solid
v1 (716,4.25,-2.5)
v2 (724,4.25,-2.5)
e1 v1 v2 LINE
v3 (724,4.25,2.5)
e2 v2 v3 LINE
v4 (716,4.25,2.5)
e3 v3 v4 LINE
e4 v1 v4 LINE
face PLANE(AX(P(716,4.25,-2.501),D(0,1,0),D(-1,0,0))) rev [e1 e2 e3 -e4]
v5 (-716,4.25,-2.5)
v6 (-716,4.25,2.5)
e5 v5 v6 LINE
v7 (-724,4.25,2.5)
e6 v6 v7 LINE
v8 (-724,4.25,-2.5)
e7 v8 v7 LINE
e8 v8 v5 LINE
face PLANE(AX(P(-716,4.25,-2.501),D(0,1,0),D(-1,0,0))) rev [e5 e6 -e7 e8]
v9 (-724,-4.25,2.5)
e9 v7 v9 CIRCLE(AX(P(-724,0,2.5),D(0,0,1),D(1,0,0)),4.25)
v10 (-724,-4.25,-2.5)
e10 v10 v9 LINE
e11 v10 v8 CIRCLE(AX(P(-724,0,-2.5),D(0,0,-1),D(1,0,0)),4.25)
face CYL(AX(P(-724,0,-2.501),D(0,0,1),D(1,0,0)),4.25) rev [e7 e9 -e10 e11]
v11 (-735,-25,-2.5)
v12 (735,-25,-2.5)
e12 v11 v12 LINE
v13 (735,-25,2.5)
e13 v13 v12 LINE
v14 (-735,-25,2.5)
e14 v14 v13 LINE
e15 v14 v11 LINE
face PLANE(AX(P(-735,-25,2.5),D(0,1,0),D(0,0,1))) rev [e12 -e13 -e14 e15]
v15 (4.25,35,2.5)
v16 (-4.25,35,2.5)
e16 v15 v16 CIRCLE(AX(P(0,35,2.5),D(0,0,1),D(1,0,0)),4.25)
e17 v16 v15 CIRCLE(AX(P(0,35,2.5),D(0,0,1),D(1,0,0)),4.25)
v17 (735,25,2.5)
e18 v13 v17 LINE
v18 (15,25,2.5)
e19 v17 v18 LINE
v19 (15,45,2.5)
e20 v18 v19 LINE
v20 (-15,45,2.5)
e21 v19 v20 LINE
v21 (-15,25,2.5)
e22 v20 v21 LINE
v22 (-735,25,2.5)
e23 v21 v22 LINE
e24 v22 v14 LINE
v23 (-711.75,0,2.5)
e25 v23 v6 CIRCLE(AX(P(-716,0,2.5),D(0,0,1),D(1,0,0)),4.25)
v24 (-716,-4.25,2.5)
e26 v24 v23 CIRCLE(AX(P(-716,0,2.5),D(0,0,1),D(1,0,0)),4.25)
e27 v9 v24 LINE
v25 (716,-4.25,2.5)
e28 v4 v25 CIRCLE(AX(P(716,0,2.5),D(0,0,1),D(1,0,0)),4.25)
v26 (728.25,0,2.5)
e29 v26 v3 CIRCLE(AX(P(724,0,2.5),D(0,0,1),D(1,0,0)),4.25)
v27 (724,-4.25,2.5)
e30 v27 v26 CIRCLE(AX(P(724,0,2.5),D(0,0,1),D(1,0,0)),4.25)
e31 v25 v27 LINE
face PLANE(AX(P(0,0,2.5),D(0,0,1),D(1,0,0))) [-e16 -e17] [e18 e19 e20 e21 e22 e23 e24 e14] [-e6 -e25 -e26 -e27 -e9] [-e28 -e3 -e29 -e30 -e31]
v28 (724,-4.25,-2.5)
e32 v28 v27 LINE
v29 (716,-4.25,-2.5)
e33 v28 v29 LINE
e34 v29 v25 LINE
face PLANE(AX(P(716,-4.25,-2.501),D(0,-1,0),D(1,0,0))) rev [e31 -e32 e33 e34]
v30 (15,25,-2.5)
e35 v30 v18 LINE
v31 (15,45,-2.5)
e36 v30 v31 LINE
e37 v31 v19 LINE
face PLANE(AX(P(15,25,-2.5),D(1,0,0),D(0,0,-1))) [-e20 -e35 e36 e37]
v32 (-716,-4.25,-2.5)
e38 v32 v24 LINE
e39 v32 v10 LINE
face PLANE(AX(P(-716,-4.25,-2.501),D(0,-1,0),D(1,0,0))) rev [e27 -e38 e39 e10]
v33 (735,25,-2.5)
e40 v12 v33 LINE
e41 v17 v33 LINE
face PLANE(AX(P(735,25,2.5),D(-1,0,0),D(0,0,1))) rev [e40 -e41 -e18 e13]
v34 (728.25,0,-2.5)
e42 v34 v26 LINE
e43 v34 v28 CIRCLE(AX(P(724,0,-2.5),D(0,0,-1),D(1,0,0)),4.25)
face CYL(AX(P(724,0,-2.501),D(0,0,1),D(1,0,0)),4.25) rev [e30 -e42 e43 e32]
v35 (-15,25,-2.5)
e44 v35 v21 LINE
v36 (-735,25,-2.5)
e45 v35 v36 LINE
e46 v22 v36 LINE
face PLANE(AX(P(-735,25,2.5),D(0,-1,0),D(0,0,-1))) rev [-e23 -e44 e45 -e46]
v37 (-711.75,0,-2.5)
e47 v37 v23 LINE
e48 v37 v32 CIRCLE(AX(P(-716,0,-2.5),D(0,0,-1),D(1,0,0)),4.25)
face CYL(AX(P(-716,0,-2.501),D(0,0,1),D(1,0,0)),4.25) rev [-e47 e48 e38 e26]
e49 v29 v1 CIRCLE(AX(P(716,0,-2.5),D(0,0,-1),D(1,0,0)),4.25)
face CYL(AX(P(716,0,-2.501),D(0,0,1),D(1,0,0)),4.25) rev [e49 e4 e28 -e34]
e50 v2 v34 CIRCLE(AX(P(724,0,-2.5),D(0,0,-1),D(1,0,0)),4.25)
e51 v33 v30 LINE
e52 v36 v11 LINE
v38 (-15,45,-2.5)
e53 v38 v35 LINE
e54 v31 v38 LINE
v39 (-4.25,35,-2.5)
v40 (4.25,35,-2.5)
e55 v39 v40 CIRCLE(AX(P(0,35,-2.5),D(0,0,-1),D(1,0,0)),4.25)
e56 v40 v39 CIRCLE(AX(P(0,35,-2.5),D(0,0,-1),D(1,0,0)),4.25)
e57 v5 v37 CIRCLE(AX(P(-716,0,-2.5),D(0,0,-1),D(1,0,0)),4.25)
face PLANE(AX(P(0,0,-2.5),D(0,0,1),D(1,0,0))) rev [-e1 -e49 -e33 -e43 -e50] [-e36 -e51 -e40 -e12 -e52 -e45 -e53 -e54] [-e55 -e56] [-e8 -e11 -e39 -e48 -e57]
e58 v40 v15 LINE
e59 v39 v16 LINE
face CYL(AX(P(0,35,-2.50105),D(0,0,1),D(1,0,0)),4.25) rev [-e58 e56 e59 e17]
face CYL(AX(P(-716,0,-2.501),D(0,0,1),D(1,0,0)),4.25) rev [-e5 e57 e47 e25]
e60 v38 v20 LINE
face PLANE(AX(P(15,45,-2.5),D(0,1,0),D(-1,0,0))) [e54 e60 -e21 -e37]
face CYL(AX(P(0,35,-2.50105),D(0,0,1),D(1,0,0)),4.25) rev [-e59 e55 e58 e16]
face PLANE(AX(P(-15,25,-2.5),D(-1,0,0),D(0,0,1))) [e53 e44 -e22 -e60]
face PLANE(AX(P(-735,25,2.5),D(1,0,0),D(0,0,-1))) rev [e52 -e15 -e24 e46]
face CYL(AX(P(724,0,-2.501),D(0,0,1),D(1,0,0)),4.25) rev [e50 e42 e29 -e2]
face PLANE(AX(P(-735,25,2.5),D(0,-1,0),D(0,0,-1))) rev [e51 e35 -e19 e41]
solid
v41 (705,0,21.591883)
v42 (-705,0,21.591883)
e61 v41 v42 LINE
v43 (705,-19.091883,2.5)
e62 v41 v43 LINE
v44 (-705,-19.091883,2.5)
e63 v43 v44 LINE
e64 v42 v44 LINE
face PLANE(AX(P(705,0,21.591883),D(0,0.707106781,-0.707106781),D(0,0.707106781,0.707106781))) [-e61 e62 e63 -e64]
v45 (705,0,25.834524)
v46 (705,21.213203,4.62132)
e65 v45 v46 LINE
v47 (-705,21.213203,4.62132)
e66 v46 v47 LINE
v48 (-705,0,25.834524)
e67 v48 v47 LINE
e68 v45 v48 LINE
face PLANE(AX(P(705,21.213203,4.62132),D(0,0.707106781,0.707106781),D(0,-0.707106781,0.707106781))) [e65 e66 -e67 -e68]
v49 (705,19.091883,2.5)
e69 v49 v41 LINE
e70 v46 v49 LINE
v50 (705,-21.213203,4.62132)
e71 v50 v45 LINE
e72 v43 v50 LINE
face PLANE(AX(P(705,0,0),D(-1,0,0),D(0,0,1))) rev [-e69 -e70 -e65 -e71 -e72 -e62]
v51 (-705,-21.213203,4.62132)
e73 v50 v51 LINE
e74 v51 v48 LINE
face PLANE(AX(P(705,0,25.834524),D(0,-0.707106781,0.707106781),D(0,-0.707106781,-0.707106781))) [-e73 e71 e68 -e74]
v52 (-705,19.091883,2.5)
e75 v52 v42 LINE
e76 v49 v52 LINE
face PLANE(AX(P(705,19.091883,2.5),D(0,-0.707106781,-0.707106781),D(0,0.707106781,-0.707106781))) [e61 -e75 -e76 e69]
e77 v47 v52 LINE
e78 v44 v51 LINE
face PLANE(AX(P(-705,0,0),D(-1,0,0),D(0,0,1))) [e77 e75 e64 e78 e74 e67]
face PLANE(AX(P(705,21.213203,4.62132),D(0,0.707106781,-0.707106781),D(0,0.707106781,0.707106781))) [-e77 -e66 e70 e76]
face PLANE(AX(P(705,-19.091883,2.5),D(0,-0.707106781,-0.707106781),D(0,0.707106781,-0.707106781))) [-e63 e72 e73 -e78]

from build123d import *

# Parameters (mm, degrees)
SKETCH_1_W          = 1470
SKETCH_1_H          = 50
EXTRUDE_1_DEPTH     = 2.5
EXTRUDE_2_DEPTH     = 1410
CUT_EXTRUDE_1_DEPTH = 5
SKETCH_5_W          = 30
SKETCH_5_H          = 20
EXTRUDE_3_DEPTH     = 5
SKETCH_6_R          = 4.25
CUT_EXTRUDE_2_DEPTH = 5


with BuildPart() as part:
    # 草图1 → 凸台-拉伸1 (new, symmetric)
    with BuildSketch(Plane.XY):
        Rectangle(SKETCH_1_W, SKETCH_1_H)
    extrude(amount=EXTRUDE_1_DEPTH, both=True)

    # 草图4 → 切除-拉伸1 (cut)
    with BuildSketch(Plane.XY.offset(2.5)):
        with BuildLine():
            Line((716, 4.25), (724, 4.25))
            ThreePointArc((724, 4.25), (728.25, 0), (724, -4.25))
            Line((724, -4.25), (716, -4.25))
            ThreePointArc((716, -4.25), (711.75, 0), (716, 4.25))
        make_face()
        with BuildLine():
            Line((-716, -4.25), (-724, -4.25))
            ThreePointArc((-724, -4.25), (-728.25, 0), (-724, 4.25))
            Line((-724, 4.25), (-716, 4.25))
            ThreePointArc((-716, 4.25), (-711.75, 0), (-716, -4.25))
        make_face()
    extrude(amount=-CUT_EXTRUDE_1_DEPTH, mode=Mode.SUBTRACT)

    # 草图5 → 凸台-拉伸3 (add)
    with BuildSketch(Plane.XY.offset(2.5)):
        with Locations((0, 35)):
            Rectangle(SKETCH_5_W, SKETCH_5_H)
    extrude(amount=-EXTRUDE_3_DEPTH)

    # 草图6 → 切除-拉伸2 (cut)
    with BuildSketch(Plane.XY.offset(2.5)):
        with Locations((0, 35)):
            Circle(SKETCH_6_R)
    extrude(amount=-CUT_EXTRUDE_2_DEPTH, mode=Mode.SUBTRACT)


with BuildPart() as body_2:
    # 草图3 → 凸台-拉伸2 (new body)
    with BuildSketch(Plane.ZY.offset(705)):
        Polygon((2.5, 19.091883092), (21.591883092, 0), (2.5, -19.091883092), (4.621320344, -21.213203436), (25.834523779, 0), (4.621320344, 21.213203436), align=None)
    extrude(amount=-EXTRUDE_2_DEPTH)


solid = Compound([part.part, body_2.part])
